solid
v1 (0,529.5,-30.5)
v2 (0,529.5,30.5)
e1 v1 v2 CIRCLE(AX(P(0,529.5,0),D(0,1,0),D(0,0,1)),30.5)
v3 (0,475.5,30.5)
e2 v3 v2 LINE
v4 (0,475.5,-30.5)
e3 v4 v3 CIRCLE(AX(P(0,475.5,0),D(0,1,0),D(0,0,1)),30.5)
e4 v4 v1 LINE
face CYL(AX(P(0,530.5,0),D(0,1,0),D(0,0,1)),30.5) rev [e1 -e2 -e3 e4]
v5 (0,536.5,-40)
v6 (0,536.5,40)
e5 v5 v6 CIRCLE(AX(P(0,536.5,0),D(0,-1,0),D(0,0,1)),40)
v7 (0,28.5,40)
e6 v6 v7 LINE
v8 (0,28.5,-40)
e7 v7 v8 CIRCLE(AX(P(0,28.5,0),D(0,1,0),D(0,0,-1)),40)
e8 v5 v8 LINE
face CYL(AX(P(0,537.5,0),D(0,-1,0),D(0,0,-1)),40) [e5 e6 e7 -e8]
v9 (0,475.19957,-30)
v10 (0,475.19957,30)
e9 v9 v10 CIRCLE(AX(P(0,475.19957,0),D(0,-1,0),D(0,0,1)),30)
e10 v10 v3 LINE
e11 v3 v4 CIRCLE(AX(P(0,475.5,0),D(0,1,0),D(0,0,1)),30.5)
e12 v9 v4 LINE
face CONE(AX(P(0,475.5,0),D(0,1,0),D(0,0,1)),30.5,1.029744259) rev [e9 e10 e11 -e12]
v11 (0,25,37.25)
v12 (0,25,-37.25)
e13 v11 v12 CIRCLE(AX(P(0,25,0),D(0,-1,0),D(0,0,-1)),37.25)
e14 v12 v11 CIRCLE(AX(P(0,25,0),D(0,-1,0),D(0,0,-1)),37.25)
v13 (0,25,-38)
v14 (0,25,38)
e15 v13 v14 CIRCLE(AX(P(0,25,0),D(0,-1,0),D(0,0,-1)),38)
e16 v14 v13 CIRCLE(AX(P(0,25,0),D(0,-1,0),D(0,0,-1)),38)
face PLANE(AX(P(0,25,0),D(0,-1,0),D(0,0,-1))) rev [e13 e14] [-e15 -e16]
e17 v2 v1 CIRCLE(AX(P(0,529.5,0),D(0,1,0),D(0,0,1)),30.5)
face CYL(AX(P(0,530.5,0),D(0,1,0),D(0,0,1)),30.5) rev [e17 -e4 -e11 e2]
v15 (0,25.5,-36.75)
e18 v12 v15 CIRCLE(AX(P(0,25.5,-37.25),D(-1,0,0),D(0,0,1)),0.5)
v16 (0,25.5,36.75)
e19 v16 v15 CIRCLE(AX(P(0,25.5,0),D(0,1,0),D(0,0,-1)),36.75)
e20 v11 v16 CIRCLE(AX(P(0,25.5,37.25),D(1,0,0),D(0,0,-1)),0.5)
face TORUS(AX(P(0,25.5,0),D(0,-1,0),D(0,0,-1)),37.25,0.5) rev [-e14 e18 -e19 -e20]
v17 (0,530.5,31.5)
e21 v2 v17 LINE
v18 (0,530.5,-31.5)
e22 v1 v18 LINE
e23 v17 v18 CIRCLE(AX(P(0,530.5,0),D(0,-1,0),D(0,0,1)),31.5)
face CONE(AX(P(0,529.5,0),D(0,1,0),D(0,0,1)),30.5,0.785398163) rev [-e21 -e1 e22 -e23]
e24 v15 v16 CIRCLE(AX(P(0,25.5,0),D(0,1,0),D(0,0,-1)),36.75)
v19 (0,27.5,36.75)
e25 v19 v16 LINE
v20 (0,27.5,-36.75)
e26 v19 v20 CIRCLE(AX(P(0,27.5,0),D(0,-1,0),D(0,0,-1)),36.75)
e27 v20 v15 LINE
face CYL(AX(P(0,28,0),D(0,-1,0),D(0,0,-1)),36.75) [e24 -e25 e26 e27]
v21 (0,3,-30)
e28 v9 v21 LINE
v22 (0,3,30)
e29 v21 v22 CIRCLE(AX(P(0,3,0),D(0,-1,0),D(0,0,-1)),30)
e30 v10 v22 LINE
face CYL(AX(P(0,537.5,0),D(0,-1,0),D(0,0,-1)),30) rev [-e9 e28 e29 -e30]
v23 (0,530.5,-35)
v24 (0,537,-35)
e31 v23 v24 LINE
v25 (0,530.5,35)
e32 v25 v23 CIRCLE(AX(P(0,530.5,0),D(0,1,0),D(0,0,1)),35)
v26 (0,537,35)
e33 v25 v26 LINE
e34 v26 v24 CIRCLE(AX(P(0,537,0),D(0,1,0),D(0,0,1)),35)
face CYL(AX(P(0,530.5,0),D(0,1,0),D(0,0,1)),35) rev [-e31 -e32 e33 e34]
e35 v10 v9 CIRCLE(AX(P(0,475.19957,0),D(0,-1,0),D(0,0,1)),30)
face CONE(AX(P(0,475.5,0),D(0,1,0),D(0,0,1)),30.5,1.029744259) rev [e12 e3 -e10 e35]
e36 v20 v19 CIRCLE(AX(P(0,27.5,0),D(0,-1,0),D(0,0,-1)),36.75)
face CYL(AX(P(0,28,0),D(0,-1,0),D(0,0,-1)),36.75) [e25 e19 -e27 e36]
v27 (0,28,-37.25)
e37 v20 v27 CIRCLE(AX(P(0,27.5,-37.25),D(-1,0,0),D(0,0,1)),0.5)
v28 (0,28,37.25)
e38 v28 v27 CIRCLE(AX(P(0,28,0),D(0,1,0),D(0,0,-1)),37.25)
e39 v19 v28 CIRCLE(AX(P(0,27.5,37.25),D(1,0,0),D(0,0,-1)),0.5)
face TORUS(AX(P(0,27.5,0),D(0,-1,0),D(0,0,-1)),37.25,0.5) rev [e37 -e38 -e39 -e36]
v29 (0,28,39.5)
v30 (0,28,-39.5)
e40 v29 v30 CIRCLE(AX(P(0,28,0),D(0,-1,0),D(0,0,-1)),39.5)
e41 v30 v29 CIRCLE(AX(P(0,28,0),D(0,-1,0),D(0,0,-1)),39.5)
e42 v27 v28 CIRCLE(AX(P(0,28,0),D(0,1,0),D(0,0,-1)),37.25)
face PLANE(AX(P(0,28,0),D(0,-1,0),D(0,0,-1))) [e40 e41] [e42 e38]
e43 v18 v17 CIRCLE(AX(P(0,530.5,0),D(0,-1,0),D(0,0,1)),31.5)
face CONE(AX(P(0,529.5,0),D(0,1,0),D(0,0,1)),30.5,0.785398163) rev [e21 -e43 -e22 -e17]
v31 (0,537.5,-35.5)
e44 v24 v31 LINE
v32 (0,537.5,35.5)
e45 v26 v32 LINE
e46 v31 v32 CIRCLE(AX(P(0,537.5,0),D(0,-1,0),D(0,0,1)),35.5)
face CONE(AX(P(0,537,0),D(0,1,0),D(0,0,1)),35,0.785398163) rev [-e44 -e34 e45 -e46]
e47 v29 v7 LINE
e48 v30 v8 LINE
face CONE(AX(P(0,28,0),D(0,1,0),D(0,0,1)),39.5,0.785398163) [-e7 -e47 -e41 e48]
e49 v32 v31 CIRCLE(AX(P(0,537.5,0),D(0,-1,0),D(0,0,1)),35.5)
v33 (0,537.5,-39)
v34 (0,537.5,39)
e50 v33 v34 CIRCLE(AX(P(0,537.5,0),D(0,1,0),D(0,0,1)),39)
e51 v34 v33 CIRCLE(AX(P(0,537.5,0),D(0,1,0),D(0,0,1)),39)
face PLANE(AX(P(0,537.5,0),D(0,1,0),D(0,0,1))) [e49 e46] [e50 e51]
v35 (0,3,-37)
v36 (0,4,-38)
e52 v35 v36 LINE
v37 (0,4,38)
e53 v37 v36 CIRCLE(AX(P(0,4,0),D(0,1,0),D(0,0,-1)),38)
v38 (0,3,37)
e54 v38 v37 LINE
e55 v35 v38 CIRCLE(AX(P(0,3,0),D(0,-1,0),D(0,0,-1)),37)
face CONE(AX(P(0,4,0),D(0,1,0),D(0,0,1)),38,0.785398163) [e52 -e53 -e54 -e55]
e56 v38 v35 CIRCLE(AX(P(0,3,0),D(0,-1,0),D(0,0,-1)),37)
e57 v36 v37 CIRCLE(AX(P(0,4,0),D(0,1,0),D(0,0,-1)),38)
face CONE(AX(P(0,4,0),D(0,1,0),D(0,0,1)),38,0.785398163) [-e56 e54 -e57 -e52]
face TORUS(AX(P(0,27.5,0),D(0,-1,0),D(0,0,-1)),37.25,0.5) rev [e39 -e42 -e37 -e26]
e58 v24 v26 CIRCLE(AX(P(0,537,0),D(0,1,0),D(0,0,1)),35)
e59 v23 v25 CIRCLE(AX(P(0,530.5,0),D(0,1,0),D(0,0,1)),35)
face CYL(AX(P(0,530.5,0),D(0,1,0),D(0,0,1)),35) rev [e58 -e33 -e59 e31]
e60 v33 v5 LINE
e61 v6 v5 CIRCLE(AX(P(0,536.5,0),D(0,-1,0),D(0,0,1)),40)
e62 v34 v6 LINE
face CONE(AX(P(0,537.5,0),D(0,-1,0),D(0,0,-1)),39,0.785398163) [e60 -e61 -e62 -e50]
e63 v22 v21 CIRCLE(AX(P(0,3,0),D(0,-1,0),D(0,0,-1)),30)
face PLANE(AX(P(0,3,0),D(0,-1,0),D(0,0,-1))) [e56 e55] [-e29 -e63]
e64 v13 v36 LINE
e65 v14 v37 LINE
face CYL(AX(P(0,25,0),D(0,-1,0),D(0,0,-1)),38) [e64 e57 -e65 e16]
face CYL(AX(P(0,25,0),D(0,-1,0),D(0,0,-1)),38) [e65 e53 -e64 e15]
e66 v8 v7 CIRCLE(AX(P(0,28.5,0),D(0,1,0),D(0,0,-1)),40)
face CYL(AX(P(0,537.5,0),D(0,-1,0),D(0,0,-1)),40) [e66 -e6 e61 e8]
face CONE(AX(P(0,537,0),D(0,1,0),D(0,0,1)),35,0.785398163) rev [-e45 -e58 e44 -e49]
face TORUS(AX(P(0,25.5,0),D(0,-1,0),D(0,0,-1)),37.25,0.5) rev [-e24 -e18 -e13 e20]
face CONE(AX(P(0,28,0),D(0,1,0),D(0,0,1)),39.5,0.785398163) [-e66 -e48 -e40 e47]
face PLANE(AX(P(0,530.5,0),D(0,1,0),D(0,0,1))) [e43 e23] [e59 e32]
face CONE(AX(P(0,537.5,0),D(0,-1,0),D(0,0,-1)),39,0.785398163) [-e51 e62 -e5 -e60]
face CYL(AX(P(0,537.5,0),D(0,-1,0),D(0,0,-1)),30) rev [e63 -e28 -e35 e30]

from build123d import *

# Parameters (mm, degrees)
SKETCH1_R                  = 40
SKETCH1_R_2                = 30
BOSS_EXTRUDE1_DEPTH        = 537.5
CUT_EXTRUDE1_START         = -25
SKETCH2_R                  = 55.029082457
SKETCH2_R_2                = 36.75
CUT_EXTRUDE1_DEPTH         = 3
SKETCH3_R                  = 40
SKETCH3_R_2                = 38
CUT_EXTRUDE2_DEPTH         = 25
CHAMFER1_SIZE              = 1
SKETCH4_R                  = 33.575067705
BOSS_EXTRUDE2_DEPTH        = 40
SKETCH5_R                  = 25
CUT_EXTRUDE3_DEPTH         = 6
SKETCH6_R                  = 21.5
CUT_EXTRUDE4_DEPTH         = 535.501870904
CHAMFER2_SIZE              = 1
SKETCH9_R                  = 30
CUT_EXTRUDE7_DEPTH         = 40
SKETCH10_R                 = 35
CUT_EXTRUDE8_DEPTH         = 7
M64X4_0_TAPPED_HOLE1_D     = 60
M64X4_0_TAPPED_HOLE1_DEPTH = 20
M64X4_0_TAPPED_HOLE1_TIP   = 18.025818571
CHAMFER3_SIZE              = 0.5
CHAMFER4_SIZE              = 0.5
SKETCH13_R                 = 40
CUT_EXTRUDE9_DEPTH         = 3
CHAMFER5_SIZE              = 1
CHAMFER7_SIZE              = 0.5
FILLET1_R                  = 0.5
M64X3_0_TAPPED_HOLE1_D     = 61
M64X3_0_TAPPED_HOLE1_DEPTH = 55
M64X3_0_TAPPED_HOLE1_TIP   = 18.32624888
CHAMFER8_SIZE              = 1


with BuildPart() as part:
    # Sketch1 → Boss-Extrude1 (new body)
    with BuildSketch(Plane(origin=(0, 0, 0), x_dir=(1, 0, 0), z_dir=(0, 1, 0))):
        with Locations(Location((0, 0, 0), (0, 0, 270))):
            Circle(SKETCH1_R)
        with Locations(Location((0, 0, 0), (0, 0, 270))):
            Circle(SKETCH1_R_2, mode=Mode.SUBTRACT)
    extrude(amount=BOSS_EXTRUDE1_DEPTH)

    # Sketch2 → Cut-Extrude1 (cut)
    with BuildSketch(Plane.XZ.offset(CUT_EXTRUDE1_START)):
        Circle(SKETCH2_R)
        with Locations(Location((0, 0, 0), (0, 0, 270))):
            Circle(SKETCH2_R_2, mode=Mode.SUBTRACT)
    extrude(amount=-CUT_EXTRUDE1_DEPTH, mode=Mode.SUBTRACT)

    # Sketch3 → Cut-Extrude2 (cut)
    with BuildSketch(Plane.XZ):
        with Locations(Location((0, 0, 0), (0, 0, 270))):
            Circle(SKETCH3_R)
        with Locations(Location((0, 0, 0), (0, 0, 270))):
            Circle(SKETCH3_R_2, mode=Mode.SUBTRACT)
    extrude(amount=-CUT_EXTRUDE2_DEPTH, mode=Mode.SUBTRACT)

    # Chamfer1
    chamfer1_edges = [part.edges().sort_by_distance(p)[0] for p in [
        (0, 0, 38),
        (0, 537.5, -40),
    ]]
    chamfer(chamfer1_edges, length=CHAMFER1_SIZE)

    # Sketch4 → Boss-Extrude2 (add)
    with BuildSketch(Plane(origin=(0, 537.5, 0), x_dir=(1, 0, 0), z_dir=(0, 1, 0))):
        Circle(SKETCH4_R)
    extrude(amount=-BOSS_EXTRUDE2_DEPTH)

    # Sketch5 → Cut-Extrude3 (cut)
    with BuildSketch(Plane(origin=(0, 537.5, 0), x_dir=(1, 0, 0), z_dir=(0, 1, 0))):
        with Locations(Location((0, 0, 0), (0, 0, 270))):
            Circle(SKETCH5_R)
    extrude(amount=-CUT_EXTRUDE3_DEPTH, mode=Mode.SUBTRACT)

    # Sketch6 → Cut-Extrude4 (cut, through all)
    with BuildSketch(Plane(origin=(0, 531.5, 0), x_dir=(1, 0, 0), z_dir=(0, 1, 0))):
        with Locations(Location((0, 0, 0), (0, 0, 270))):
            Circle(SKETCH6_R)
    extrude(amount=-CUT_EXTRUDE4_DEPTH, mode=Mode.SUBTRACT)

    # Chamfer2
    chamfer2_edges = [part.edges().sort_by_distance(p)[0] for p in [
        (0, 531.5, -21.5),
    ]]
    chamfer(chamfer2_edges, length=CHAMFER2_SIZE)

    # Sketch9 → Cut-Extrude7 (cut)
    with BuildSketch(Plane.XZ.offset(-497.5)):
        with Locations(Location((0, 0, 0), (0, 0, 90))):
            Circle(SKETCH9_R)
    extrude(amount=-CUT_EXTRUDE7_DEPTH, mode=Mode.SUBTRACT)

    # Sketch10 → Cut-Extrude8 (cut)
    with BuildSketch(Plane(origin=(0, 537.5, 0), x_dir=(1, 0, 0), z_dir=(0, 1, 0))):
        with Locations(Location((0, 0, 0), (0, 0, 270))):
            Circle(SKETCH10_R)
    extrude(amount=-CUT_EXTRUDE8_DEPTH, mode=Mode.SUBTRACT)

    # M64x4.0 Tapped Hole1
    with Locations(Plane(origin=(0, 530.5, 0), x_dir=(1, 0, 0), z_dir=(0, 1, 0))):
        with Locations((0, 0)):
            Hole(M64X4_0_TAPPED_HOLE1_D / 2, depth=M64X4_0_TAPPED_HOLE1_DEPTH)
            with Locations((0, 0, -(M64X4_0_TAPPED_HOLE1_DEPTH + M64X4_0_TAPPED_HOLE1_TIP / 2))):  # 118° drill point
                Cone(0, M64X4_0_TAPPED_HOLE1_D / 2, M64X4_0_TAPPED_HOLE1_TIP, mode=Mode.SUBTRACT)

    # Chamfer3
    chamfer3_edges = [part.edges().sort_by_distance(p)[0] for p in [
        (0, 537.5, -35),
    ]]
    chamfer(chamfer3_edges, length=CHAMFER3_SIZE)

    # Chamfer4
    chamfer4_edges = [part.edges().sort_by_distance(p)[0] for p in [
        (0, 530.5, -30),
    ]]
    chamfer(chamfer4_edges, length=CHAMFER4_SIZE)

    # Sketch13 → Cut-Extrude9 (cut)
    with BuildSketch(Plane.XZ):
        with Locations(Location((0, 0, 0), (0, 0, 270))):
            Circle(SKETCH13_R)
    extrude(amount=-CUT_EXTRUDE9_DEPTH, mode=Mode.SUBTRACT)

    # Chamfer5
    chamfer5_edges = [part.edges().sort_by_distance(p)[0] for p in [
        (0, 3, 38),
    ]]
    chamfer(chamfer5_edges, length=CHAMFER5_SIZE)

    # Chamfer7
    chamfer7_edges = [part.edges().sort_by_distance(p)[0] for p in [
        (0, 28, -40),
    ]]
    chamfer(chamfer7_edges, length=CHAMFER7_SIZE)

    # Fillet1
    fillet1_edges = [part.edges().sort_by_distance(p)[0] for p in [
        (0, 28, 36.75),
        (0, 25, 36.75),
    ]]
    fillet(fillet1_edges, radius=FILLET1_R)

    # M64x3.0 Tapped Hole1
    with Locations(Plane(origin=(0, 530.5, 0), x_dir=(1, 0, 0), z_dir=(0, 1, 0))):
        with Locations((0, 0)):
            Hole(M64X3_0_TAPPED_HOLE1_D / 2, depth=M64X3_0_TAPPED_HOLE1_DEPTH)
            with Locations((0, 0, -(M64X3_0_TAPPED_HOLE1_DEPTH + M64X3_0_TAPPED_HOLE1_TIP / 2))):  # 118° drill point
                Cone(0, M64X3_0_TAPPED_HOLE1_D / 2, M64X3_0_TAPPED_HOLE1_TIP, mode=Mode.SUBTRACT)

    # Chamfer8
    chamfer8_edges = [part.edges().sort_by_distance(p)[0] for p in [
        (30.5, 530.5, 0),
    ]]
    chamfer(chamfer8_edges, length=CHAMFER8_SIZE)


solid = part.part
